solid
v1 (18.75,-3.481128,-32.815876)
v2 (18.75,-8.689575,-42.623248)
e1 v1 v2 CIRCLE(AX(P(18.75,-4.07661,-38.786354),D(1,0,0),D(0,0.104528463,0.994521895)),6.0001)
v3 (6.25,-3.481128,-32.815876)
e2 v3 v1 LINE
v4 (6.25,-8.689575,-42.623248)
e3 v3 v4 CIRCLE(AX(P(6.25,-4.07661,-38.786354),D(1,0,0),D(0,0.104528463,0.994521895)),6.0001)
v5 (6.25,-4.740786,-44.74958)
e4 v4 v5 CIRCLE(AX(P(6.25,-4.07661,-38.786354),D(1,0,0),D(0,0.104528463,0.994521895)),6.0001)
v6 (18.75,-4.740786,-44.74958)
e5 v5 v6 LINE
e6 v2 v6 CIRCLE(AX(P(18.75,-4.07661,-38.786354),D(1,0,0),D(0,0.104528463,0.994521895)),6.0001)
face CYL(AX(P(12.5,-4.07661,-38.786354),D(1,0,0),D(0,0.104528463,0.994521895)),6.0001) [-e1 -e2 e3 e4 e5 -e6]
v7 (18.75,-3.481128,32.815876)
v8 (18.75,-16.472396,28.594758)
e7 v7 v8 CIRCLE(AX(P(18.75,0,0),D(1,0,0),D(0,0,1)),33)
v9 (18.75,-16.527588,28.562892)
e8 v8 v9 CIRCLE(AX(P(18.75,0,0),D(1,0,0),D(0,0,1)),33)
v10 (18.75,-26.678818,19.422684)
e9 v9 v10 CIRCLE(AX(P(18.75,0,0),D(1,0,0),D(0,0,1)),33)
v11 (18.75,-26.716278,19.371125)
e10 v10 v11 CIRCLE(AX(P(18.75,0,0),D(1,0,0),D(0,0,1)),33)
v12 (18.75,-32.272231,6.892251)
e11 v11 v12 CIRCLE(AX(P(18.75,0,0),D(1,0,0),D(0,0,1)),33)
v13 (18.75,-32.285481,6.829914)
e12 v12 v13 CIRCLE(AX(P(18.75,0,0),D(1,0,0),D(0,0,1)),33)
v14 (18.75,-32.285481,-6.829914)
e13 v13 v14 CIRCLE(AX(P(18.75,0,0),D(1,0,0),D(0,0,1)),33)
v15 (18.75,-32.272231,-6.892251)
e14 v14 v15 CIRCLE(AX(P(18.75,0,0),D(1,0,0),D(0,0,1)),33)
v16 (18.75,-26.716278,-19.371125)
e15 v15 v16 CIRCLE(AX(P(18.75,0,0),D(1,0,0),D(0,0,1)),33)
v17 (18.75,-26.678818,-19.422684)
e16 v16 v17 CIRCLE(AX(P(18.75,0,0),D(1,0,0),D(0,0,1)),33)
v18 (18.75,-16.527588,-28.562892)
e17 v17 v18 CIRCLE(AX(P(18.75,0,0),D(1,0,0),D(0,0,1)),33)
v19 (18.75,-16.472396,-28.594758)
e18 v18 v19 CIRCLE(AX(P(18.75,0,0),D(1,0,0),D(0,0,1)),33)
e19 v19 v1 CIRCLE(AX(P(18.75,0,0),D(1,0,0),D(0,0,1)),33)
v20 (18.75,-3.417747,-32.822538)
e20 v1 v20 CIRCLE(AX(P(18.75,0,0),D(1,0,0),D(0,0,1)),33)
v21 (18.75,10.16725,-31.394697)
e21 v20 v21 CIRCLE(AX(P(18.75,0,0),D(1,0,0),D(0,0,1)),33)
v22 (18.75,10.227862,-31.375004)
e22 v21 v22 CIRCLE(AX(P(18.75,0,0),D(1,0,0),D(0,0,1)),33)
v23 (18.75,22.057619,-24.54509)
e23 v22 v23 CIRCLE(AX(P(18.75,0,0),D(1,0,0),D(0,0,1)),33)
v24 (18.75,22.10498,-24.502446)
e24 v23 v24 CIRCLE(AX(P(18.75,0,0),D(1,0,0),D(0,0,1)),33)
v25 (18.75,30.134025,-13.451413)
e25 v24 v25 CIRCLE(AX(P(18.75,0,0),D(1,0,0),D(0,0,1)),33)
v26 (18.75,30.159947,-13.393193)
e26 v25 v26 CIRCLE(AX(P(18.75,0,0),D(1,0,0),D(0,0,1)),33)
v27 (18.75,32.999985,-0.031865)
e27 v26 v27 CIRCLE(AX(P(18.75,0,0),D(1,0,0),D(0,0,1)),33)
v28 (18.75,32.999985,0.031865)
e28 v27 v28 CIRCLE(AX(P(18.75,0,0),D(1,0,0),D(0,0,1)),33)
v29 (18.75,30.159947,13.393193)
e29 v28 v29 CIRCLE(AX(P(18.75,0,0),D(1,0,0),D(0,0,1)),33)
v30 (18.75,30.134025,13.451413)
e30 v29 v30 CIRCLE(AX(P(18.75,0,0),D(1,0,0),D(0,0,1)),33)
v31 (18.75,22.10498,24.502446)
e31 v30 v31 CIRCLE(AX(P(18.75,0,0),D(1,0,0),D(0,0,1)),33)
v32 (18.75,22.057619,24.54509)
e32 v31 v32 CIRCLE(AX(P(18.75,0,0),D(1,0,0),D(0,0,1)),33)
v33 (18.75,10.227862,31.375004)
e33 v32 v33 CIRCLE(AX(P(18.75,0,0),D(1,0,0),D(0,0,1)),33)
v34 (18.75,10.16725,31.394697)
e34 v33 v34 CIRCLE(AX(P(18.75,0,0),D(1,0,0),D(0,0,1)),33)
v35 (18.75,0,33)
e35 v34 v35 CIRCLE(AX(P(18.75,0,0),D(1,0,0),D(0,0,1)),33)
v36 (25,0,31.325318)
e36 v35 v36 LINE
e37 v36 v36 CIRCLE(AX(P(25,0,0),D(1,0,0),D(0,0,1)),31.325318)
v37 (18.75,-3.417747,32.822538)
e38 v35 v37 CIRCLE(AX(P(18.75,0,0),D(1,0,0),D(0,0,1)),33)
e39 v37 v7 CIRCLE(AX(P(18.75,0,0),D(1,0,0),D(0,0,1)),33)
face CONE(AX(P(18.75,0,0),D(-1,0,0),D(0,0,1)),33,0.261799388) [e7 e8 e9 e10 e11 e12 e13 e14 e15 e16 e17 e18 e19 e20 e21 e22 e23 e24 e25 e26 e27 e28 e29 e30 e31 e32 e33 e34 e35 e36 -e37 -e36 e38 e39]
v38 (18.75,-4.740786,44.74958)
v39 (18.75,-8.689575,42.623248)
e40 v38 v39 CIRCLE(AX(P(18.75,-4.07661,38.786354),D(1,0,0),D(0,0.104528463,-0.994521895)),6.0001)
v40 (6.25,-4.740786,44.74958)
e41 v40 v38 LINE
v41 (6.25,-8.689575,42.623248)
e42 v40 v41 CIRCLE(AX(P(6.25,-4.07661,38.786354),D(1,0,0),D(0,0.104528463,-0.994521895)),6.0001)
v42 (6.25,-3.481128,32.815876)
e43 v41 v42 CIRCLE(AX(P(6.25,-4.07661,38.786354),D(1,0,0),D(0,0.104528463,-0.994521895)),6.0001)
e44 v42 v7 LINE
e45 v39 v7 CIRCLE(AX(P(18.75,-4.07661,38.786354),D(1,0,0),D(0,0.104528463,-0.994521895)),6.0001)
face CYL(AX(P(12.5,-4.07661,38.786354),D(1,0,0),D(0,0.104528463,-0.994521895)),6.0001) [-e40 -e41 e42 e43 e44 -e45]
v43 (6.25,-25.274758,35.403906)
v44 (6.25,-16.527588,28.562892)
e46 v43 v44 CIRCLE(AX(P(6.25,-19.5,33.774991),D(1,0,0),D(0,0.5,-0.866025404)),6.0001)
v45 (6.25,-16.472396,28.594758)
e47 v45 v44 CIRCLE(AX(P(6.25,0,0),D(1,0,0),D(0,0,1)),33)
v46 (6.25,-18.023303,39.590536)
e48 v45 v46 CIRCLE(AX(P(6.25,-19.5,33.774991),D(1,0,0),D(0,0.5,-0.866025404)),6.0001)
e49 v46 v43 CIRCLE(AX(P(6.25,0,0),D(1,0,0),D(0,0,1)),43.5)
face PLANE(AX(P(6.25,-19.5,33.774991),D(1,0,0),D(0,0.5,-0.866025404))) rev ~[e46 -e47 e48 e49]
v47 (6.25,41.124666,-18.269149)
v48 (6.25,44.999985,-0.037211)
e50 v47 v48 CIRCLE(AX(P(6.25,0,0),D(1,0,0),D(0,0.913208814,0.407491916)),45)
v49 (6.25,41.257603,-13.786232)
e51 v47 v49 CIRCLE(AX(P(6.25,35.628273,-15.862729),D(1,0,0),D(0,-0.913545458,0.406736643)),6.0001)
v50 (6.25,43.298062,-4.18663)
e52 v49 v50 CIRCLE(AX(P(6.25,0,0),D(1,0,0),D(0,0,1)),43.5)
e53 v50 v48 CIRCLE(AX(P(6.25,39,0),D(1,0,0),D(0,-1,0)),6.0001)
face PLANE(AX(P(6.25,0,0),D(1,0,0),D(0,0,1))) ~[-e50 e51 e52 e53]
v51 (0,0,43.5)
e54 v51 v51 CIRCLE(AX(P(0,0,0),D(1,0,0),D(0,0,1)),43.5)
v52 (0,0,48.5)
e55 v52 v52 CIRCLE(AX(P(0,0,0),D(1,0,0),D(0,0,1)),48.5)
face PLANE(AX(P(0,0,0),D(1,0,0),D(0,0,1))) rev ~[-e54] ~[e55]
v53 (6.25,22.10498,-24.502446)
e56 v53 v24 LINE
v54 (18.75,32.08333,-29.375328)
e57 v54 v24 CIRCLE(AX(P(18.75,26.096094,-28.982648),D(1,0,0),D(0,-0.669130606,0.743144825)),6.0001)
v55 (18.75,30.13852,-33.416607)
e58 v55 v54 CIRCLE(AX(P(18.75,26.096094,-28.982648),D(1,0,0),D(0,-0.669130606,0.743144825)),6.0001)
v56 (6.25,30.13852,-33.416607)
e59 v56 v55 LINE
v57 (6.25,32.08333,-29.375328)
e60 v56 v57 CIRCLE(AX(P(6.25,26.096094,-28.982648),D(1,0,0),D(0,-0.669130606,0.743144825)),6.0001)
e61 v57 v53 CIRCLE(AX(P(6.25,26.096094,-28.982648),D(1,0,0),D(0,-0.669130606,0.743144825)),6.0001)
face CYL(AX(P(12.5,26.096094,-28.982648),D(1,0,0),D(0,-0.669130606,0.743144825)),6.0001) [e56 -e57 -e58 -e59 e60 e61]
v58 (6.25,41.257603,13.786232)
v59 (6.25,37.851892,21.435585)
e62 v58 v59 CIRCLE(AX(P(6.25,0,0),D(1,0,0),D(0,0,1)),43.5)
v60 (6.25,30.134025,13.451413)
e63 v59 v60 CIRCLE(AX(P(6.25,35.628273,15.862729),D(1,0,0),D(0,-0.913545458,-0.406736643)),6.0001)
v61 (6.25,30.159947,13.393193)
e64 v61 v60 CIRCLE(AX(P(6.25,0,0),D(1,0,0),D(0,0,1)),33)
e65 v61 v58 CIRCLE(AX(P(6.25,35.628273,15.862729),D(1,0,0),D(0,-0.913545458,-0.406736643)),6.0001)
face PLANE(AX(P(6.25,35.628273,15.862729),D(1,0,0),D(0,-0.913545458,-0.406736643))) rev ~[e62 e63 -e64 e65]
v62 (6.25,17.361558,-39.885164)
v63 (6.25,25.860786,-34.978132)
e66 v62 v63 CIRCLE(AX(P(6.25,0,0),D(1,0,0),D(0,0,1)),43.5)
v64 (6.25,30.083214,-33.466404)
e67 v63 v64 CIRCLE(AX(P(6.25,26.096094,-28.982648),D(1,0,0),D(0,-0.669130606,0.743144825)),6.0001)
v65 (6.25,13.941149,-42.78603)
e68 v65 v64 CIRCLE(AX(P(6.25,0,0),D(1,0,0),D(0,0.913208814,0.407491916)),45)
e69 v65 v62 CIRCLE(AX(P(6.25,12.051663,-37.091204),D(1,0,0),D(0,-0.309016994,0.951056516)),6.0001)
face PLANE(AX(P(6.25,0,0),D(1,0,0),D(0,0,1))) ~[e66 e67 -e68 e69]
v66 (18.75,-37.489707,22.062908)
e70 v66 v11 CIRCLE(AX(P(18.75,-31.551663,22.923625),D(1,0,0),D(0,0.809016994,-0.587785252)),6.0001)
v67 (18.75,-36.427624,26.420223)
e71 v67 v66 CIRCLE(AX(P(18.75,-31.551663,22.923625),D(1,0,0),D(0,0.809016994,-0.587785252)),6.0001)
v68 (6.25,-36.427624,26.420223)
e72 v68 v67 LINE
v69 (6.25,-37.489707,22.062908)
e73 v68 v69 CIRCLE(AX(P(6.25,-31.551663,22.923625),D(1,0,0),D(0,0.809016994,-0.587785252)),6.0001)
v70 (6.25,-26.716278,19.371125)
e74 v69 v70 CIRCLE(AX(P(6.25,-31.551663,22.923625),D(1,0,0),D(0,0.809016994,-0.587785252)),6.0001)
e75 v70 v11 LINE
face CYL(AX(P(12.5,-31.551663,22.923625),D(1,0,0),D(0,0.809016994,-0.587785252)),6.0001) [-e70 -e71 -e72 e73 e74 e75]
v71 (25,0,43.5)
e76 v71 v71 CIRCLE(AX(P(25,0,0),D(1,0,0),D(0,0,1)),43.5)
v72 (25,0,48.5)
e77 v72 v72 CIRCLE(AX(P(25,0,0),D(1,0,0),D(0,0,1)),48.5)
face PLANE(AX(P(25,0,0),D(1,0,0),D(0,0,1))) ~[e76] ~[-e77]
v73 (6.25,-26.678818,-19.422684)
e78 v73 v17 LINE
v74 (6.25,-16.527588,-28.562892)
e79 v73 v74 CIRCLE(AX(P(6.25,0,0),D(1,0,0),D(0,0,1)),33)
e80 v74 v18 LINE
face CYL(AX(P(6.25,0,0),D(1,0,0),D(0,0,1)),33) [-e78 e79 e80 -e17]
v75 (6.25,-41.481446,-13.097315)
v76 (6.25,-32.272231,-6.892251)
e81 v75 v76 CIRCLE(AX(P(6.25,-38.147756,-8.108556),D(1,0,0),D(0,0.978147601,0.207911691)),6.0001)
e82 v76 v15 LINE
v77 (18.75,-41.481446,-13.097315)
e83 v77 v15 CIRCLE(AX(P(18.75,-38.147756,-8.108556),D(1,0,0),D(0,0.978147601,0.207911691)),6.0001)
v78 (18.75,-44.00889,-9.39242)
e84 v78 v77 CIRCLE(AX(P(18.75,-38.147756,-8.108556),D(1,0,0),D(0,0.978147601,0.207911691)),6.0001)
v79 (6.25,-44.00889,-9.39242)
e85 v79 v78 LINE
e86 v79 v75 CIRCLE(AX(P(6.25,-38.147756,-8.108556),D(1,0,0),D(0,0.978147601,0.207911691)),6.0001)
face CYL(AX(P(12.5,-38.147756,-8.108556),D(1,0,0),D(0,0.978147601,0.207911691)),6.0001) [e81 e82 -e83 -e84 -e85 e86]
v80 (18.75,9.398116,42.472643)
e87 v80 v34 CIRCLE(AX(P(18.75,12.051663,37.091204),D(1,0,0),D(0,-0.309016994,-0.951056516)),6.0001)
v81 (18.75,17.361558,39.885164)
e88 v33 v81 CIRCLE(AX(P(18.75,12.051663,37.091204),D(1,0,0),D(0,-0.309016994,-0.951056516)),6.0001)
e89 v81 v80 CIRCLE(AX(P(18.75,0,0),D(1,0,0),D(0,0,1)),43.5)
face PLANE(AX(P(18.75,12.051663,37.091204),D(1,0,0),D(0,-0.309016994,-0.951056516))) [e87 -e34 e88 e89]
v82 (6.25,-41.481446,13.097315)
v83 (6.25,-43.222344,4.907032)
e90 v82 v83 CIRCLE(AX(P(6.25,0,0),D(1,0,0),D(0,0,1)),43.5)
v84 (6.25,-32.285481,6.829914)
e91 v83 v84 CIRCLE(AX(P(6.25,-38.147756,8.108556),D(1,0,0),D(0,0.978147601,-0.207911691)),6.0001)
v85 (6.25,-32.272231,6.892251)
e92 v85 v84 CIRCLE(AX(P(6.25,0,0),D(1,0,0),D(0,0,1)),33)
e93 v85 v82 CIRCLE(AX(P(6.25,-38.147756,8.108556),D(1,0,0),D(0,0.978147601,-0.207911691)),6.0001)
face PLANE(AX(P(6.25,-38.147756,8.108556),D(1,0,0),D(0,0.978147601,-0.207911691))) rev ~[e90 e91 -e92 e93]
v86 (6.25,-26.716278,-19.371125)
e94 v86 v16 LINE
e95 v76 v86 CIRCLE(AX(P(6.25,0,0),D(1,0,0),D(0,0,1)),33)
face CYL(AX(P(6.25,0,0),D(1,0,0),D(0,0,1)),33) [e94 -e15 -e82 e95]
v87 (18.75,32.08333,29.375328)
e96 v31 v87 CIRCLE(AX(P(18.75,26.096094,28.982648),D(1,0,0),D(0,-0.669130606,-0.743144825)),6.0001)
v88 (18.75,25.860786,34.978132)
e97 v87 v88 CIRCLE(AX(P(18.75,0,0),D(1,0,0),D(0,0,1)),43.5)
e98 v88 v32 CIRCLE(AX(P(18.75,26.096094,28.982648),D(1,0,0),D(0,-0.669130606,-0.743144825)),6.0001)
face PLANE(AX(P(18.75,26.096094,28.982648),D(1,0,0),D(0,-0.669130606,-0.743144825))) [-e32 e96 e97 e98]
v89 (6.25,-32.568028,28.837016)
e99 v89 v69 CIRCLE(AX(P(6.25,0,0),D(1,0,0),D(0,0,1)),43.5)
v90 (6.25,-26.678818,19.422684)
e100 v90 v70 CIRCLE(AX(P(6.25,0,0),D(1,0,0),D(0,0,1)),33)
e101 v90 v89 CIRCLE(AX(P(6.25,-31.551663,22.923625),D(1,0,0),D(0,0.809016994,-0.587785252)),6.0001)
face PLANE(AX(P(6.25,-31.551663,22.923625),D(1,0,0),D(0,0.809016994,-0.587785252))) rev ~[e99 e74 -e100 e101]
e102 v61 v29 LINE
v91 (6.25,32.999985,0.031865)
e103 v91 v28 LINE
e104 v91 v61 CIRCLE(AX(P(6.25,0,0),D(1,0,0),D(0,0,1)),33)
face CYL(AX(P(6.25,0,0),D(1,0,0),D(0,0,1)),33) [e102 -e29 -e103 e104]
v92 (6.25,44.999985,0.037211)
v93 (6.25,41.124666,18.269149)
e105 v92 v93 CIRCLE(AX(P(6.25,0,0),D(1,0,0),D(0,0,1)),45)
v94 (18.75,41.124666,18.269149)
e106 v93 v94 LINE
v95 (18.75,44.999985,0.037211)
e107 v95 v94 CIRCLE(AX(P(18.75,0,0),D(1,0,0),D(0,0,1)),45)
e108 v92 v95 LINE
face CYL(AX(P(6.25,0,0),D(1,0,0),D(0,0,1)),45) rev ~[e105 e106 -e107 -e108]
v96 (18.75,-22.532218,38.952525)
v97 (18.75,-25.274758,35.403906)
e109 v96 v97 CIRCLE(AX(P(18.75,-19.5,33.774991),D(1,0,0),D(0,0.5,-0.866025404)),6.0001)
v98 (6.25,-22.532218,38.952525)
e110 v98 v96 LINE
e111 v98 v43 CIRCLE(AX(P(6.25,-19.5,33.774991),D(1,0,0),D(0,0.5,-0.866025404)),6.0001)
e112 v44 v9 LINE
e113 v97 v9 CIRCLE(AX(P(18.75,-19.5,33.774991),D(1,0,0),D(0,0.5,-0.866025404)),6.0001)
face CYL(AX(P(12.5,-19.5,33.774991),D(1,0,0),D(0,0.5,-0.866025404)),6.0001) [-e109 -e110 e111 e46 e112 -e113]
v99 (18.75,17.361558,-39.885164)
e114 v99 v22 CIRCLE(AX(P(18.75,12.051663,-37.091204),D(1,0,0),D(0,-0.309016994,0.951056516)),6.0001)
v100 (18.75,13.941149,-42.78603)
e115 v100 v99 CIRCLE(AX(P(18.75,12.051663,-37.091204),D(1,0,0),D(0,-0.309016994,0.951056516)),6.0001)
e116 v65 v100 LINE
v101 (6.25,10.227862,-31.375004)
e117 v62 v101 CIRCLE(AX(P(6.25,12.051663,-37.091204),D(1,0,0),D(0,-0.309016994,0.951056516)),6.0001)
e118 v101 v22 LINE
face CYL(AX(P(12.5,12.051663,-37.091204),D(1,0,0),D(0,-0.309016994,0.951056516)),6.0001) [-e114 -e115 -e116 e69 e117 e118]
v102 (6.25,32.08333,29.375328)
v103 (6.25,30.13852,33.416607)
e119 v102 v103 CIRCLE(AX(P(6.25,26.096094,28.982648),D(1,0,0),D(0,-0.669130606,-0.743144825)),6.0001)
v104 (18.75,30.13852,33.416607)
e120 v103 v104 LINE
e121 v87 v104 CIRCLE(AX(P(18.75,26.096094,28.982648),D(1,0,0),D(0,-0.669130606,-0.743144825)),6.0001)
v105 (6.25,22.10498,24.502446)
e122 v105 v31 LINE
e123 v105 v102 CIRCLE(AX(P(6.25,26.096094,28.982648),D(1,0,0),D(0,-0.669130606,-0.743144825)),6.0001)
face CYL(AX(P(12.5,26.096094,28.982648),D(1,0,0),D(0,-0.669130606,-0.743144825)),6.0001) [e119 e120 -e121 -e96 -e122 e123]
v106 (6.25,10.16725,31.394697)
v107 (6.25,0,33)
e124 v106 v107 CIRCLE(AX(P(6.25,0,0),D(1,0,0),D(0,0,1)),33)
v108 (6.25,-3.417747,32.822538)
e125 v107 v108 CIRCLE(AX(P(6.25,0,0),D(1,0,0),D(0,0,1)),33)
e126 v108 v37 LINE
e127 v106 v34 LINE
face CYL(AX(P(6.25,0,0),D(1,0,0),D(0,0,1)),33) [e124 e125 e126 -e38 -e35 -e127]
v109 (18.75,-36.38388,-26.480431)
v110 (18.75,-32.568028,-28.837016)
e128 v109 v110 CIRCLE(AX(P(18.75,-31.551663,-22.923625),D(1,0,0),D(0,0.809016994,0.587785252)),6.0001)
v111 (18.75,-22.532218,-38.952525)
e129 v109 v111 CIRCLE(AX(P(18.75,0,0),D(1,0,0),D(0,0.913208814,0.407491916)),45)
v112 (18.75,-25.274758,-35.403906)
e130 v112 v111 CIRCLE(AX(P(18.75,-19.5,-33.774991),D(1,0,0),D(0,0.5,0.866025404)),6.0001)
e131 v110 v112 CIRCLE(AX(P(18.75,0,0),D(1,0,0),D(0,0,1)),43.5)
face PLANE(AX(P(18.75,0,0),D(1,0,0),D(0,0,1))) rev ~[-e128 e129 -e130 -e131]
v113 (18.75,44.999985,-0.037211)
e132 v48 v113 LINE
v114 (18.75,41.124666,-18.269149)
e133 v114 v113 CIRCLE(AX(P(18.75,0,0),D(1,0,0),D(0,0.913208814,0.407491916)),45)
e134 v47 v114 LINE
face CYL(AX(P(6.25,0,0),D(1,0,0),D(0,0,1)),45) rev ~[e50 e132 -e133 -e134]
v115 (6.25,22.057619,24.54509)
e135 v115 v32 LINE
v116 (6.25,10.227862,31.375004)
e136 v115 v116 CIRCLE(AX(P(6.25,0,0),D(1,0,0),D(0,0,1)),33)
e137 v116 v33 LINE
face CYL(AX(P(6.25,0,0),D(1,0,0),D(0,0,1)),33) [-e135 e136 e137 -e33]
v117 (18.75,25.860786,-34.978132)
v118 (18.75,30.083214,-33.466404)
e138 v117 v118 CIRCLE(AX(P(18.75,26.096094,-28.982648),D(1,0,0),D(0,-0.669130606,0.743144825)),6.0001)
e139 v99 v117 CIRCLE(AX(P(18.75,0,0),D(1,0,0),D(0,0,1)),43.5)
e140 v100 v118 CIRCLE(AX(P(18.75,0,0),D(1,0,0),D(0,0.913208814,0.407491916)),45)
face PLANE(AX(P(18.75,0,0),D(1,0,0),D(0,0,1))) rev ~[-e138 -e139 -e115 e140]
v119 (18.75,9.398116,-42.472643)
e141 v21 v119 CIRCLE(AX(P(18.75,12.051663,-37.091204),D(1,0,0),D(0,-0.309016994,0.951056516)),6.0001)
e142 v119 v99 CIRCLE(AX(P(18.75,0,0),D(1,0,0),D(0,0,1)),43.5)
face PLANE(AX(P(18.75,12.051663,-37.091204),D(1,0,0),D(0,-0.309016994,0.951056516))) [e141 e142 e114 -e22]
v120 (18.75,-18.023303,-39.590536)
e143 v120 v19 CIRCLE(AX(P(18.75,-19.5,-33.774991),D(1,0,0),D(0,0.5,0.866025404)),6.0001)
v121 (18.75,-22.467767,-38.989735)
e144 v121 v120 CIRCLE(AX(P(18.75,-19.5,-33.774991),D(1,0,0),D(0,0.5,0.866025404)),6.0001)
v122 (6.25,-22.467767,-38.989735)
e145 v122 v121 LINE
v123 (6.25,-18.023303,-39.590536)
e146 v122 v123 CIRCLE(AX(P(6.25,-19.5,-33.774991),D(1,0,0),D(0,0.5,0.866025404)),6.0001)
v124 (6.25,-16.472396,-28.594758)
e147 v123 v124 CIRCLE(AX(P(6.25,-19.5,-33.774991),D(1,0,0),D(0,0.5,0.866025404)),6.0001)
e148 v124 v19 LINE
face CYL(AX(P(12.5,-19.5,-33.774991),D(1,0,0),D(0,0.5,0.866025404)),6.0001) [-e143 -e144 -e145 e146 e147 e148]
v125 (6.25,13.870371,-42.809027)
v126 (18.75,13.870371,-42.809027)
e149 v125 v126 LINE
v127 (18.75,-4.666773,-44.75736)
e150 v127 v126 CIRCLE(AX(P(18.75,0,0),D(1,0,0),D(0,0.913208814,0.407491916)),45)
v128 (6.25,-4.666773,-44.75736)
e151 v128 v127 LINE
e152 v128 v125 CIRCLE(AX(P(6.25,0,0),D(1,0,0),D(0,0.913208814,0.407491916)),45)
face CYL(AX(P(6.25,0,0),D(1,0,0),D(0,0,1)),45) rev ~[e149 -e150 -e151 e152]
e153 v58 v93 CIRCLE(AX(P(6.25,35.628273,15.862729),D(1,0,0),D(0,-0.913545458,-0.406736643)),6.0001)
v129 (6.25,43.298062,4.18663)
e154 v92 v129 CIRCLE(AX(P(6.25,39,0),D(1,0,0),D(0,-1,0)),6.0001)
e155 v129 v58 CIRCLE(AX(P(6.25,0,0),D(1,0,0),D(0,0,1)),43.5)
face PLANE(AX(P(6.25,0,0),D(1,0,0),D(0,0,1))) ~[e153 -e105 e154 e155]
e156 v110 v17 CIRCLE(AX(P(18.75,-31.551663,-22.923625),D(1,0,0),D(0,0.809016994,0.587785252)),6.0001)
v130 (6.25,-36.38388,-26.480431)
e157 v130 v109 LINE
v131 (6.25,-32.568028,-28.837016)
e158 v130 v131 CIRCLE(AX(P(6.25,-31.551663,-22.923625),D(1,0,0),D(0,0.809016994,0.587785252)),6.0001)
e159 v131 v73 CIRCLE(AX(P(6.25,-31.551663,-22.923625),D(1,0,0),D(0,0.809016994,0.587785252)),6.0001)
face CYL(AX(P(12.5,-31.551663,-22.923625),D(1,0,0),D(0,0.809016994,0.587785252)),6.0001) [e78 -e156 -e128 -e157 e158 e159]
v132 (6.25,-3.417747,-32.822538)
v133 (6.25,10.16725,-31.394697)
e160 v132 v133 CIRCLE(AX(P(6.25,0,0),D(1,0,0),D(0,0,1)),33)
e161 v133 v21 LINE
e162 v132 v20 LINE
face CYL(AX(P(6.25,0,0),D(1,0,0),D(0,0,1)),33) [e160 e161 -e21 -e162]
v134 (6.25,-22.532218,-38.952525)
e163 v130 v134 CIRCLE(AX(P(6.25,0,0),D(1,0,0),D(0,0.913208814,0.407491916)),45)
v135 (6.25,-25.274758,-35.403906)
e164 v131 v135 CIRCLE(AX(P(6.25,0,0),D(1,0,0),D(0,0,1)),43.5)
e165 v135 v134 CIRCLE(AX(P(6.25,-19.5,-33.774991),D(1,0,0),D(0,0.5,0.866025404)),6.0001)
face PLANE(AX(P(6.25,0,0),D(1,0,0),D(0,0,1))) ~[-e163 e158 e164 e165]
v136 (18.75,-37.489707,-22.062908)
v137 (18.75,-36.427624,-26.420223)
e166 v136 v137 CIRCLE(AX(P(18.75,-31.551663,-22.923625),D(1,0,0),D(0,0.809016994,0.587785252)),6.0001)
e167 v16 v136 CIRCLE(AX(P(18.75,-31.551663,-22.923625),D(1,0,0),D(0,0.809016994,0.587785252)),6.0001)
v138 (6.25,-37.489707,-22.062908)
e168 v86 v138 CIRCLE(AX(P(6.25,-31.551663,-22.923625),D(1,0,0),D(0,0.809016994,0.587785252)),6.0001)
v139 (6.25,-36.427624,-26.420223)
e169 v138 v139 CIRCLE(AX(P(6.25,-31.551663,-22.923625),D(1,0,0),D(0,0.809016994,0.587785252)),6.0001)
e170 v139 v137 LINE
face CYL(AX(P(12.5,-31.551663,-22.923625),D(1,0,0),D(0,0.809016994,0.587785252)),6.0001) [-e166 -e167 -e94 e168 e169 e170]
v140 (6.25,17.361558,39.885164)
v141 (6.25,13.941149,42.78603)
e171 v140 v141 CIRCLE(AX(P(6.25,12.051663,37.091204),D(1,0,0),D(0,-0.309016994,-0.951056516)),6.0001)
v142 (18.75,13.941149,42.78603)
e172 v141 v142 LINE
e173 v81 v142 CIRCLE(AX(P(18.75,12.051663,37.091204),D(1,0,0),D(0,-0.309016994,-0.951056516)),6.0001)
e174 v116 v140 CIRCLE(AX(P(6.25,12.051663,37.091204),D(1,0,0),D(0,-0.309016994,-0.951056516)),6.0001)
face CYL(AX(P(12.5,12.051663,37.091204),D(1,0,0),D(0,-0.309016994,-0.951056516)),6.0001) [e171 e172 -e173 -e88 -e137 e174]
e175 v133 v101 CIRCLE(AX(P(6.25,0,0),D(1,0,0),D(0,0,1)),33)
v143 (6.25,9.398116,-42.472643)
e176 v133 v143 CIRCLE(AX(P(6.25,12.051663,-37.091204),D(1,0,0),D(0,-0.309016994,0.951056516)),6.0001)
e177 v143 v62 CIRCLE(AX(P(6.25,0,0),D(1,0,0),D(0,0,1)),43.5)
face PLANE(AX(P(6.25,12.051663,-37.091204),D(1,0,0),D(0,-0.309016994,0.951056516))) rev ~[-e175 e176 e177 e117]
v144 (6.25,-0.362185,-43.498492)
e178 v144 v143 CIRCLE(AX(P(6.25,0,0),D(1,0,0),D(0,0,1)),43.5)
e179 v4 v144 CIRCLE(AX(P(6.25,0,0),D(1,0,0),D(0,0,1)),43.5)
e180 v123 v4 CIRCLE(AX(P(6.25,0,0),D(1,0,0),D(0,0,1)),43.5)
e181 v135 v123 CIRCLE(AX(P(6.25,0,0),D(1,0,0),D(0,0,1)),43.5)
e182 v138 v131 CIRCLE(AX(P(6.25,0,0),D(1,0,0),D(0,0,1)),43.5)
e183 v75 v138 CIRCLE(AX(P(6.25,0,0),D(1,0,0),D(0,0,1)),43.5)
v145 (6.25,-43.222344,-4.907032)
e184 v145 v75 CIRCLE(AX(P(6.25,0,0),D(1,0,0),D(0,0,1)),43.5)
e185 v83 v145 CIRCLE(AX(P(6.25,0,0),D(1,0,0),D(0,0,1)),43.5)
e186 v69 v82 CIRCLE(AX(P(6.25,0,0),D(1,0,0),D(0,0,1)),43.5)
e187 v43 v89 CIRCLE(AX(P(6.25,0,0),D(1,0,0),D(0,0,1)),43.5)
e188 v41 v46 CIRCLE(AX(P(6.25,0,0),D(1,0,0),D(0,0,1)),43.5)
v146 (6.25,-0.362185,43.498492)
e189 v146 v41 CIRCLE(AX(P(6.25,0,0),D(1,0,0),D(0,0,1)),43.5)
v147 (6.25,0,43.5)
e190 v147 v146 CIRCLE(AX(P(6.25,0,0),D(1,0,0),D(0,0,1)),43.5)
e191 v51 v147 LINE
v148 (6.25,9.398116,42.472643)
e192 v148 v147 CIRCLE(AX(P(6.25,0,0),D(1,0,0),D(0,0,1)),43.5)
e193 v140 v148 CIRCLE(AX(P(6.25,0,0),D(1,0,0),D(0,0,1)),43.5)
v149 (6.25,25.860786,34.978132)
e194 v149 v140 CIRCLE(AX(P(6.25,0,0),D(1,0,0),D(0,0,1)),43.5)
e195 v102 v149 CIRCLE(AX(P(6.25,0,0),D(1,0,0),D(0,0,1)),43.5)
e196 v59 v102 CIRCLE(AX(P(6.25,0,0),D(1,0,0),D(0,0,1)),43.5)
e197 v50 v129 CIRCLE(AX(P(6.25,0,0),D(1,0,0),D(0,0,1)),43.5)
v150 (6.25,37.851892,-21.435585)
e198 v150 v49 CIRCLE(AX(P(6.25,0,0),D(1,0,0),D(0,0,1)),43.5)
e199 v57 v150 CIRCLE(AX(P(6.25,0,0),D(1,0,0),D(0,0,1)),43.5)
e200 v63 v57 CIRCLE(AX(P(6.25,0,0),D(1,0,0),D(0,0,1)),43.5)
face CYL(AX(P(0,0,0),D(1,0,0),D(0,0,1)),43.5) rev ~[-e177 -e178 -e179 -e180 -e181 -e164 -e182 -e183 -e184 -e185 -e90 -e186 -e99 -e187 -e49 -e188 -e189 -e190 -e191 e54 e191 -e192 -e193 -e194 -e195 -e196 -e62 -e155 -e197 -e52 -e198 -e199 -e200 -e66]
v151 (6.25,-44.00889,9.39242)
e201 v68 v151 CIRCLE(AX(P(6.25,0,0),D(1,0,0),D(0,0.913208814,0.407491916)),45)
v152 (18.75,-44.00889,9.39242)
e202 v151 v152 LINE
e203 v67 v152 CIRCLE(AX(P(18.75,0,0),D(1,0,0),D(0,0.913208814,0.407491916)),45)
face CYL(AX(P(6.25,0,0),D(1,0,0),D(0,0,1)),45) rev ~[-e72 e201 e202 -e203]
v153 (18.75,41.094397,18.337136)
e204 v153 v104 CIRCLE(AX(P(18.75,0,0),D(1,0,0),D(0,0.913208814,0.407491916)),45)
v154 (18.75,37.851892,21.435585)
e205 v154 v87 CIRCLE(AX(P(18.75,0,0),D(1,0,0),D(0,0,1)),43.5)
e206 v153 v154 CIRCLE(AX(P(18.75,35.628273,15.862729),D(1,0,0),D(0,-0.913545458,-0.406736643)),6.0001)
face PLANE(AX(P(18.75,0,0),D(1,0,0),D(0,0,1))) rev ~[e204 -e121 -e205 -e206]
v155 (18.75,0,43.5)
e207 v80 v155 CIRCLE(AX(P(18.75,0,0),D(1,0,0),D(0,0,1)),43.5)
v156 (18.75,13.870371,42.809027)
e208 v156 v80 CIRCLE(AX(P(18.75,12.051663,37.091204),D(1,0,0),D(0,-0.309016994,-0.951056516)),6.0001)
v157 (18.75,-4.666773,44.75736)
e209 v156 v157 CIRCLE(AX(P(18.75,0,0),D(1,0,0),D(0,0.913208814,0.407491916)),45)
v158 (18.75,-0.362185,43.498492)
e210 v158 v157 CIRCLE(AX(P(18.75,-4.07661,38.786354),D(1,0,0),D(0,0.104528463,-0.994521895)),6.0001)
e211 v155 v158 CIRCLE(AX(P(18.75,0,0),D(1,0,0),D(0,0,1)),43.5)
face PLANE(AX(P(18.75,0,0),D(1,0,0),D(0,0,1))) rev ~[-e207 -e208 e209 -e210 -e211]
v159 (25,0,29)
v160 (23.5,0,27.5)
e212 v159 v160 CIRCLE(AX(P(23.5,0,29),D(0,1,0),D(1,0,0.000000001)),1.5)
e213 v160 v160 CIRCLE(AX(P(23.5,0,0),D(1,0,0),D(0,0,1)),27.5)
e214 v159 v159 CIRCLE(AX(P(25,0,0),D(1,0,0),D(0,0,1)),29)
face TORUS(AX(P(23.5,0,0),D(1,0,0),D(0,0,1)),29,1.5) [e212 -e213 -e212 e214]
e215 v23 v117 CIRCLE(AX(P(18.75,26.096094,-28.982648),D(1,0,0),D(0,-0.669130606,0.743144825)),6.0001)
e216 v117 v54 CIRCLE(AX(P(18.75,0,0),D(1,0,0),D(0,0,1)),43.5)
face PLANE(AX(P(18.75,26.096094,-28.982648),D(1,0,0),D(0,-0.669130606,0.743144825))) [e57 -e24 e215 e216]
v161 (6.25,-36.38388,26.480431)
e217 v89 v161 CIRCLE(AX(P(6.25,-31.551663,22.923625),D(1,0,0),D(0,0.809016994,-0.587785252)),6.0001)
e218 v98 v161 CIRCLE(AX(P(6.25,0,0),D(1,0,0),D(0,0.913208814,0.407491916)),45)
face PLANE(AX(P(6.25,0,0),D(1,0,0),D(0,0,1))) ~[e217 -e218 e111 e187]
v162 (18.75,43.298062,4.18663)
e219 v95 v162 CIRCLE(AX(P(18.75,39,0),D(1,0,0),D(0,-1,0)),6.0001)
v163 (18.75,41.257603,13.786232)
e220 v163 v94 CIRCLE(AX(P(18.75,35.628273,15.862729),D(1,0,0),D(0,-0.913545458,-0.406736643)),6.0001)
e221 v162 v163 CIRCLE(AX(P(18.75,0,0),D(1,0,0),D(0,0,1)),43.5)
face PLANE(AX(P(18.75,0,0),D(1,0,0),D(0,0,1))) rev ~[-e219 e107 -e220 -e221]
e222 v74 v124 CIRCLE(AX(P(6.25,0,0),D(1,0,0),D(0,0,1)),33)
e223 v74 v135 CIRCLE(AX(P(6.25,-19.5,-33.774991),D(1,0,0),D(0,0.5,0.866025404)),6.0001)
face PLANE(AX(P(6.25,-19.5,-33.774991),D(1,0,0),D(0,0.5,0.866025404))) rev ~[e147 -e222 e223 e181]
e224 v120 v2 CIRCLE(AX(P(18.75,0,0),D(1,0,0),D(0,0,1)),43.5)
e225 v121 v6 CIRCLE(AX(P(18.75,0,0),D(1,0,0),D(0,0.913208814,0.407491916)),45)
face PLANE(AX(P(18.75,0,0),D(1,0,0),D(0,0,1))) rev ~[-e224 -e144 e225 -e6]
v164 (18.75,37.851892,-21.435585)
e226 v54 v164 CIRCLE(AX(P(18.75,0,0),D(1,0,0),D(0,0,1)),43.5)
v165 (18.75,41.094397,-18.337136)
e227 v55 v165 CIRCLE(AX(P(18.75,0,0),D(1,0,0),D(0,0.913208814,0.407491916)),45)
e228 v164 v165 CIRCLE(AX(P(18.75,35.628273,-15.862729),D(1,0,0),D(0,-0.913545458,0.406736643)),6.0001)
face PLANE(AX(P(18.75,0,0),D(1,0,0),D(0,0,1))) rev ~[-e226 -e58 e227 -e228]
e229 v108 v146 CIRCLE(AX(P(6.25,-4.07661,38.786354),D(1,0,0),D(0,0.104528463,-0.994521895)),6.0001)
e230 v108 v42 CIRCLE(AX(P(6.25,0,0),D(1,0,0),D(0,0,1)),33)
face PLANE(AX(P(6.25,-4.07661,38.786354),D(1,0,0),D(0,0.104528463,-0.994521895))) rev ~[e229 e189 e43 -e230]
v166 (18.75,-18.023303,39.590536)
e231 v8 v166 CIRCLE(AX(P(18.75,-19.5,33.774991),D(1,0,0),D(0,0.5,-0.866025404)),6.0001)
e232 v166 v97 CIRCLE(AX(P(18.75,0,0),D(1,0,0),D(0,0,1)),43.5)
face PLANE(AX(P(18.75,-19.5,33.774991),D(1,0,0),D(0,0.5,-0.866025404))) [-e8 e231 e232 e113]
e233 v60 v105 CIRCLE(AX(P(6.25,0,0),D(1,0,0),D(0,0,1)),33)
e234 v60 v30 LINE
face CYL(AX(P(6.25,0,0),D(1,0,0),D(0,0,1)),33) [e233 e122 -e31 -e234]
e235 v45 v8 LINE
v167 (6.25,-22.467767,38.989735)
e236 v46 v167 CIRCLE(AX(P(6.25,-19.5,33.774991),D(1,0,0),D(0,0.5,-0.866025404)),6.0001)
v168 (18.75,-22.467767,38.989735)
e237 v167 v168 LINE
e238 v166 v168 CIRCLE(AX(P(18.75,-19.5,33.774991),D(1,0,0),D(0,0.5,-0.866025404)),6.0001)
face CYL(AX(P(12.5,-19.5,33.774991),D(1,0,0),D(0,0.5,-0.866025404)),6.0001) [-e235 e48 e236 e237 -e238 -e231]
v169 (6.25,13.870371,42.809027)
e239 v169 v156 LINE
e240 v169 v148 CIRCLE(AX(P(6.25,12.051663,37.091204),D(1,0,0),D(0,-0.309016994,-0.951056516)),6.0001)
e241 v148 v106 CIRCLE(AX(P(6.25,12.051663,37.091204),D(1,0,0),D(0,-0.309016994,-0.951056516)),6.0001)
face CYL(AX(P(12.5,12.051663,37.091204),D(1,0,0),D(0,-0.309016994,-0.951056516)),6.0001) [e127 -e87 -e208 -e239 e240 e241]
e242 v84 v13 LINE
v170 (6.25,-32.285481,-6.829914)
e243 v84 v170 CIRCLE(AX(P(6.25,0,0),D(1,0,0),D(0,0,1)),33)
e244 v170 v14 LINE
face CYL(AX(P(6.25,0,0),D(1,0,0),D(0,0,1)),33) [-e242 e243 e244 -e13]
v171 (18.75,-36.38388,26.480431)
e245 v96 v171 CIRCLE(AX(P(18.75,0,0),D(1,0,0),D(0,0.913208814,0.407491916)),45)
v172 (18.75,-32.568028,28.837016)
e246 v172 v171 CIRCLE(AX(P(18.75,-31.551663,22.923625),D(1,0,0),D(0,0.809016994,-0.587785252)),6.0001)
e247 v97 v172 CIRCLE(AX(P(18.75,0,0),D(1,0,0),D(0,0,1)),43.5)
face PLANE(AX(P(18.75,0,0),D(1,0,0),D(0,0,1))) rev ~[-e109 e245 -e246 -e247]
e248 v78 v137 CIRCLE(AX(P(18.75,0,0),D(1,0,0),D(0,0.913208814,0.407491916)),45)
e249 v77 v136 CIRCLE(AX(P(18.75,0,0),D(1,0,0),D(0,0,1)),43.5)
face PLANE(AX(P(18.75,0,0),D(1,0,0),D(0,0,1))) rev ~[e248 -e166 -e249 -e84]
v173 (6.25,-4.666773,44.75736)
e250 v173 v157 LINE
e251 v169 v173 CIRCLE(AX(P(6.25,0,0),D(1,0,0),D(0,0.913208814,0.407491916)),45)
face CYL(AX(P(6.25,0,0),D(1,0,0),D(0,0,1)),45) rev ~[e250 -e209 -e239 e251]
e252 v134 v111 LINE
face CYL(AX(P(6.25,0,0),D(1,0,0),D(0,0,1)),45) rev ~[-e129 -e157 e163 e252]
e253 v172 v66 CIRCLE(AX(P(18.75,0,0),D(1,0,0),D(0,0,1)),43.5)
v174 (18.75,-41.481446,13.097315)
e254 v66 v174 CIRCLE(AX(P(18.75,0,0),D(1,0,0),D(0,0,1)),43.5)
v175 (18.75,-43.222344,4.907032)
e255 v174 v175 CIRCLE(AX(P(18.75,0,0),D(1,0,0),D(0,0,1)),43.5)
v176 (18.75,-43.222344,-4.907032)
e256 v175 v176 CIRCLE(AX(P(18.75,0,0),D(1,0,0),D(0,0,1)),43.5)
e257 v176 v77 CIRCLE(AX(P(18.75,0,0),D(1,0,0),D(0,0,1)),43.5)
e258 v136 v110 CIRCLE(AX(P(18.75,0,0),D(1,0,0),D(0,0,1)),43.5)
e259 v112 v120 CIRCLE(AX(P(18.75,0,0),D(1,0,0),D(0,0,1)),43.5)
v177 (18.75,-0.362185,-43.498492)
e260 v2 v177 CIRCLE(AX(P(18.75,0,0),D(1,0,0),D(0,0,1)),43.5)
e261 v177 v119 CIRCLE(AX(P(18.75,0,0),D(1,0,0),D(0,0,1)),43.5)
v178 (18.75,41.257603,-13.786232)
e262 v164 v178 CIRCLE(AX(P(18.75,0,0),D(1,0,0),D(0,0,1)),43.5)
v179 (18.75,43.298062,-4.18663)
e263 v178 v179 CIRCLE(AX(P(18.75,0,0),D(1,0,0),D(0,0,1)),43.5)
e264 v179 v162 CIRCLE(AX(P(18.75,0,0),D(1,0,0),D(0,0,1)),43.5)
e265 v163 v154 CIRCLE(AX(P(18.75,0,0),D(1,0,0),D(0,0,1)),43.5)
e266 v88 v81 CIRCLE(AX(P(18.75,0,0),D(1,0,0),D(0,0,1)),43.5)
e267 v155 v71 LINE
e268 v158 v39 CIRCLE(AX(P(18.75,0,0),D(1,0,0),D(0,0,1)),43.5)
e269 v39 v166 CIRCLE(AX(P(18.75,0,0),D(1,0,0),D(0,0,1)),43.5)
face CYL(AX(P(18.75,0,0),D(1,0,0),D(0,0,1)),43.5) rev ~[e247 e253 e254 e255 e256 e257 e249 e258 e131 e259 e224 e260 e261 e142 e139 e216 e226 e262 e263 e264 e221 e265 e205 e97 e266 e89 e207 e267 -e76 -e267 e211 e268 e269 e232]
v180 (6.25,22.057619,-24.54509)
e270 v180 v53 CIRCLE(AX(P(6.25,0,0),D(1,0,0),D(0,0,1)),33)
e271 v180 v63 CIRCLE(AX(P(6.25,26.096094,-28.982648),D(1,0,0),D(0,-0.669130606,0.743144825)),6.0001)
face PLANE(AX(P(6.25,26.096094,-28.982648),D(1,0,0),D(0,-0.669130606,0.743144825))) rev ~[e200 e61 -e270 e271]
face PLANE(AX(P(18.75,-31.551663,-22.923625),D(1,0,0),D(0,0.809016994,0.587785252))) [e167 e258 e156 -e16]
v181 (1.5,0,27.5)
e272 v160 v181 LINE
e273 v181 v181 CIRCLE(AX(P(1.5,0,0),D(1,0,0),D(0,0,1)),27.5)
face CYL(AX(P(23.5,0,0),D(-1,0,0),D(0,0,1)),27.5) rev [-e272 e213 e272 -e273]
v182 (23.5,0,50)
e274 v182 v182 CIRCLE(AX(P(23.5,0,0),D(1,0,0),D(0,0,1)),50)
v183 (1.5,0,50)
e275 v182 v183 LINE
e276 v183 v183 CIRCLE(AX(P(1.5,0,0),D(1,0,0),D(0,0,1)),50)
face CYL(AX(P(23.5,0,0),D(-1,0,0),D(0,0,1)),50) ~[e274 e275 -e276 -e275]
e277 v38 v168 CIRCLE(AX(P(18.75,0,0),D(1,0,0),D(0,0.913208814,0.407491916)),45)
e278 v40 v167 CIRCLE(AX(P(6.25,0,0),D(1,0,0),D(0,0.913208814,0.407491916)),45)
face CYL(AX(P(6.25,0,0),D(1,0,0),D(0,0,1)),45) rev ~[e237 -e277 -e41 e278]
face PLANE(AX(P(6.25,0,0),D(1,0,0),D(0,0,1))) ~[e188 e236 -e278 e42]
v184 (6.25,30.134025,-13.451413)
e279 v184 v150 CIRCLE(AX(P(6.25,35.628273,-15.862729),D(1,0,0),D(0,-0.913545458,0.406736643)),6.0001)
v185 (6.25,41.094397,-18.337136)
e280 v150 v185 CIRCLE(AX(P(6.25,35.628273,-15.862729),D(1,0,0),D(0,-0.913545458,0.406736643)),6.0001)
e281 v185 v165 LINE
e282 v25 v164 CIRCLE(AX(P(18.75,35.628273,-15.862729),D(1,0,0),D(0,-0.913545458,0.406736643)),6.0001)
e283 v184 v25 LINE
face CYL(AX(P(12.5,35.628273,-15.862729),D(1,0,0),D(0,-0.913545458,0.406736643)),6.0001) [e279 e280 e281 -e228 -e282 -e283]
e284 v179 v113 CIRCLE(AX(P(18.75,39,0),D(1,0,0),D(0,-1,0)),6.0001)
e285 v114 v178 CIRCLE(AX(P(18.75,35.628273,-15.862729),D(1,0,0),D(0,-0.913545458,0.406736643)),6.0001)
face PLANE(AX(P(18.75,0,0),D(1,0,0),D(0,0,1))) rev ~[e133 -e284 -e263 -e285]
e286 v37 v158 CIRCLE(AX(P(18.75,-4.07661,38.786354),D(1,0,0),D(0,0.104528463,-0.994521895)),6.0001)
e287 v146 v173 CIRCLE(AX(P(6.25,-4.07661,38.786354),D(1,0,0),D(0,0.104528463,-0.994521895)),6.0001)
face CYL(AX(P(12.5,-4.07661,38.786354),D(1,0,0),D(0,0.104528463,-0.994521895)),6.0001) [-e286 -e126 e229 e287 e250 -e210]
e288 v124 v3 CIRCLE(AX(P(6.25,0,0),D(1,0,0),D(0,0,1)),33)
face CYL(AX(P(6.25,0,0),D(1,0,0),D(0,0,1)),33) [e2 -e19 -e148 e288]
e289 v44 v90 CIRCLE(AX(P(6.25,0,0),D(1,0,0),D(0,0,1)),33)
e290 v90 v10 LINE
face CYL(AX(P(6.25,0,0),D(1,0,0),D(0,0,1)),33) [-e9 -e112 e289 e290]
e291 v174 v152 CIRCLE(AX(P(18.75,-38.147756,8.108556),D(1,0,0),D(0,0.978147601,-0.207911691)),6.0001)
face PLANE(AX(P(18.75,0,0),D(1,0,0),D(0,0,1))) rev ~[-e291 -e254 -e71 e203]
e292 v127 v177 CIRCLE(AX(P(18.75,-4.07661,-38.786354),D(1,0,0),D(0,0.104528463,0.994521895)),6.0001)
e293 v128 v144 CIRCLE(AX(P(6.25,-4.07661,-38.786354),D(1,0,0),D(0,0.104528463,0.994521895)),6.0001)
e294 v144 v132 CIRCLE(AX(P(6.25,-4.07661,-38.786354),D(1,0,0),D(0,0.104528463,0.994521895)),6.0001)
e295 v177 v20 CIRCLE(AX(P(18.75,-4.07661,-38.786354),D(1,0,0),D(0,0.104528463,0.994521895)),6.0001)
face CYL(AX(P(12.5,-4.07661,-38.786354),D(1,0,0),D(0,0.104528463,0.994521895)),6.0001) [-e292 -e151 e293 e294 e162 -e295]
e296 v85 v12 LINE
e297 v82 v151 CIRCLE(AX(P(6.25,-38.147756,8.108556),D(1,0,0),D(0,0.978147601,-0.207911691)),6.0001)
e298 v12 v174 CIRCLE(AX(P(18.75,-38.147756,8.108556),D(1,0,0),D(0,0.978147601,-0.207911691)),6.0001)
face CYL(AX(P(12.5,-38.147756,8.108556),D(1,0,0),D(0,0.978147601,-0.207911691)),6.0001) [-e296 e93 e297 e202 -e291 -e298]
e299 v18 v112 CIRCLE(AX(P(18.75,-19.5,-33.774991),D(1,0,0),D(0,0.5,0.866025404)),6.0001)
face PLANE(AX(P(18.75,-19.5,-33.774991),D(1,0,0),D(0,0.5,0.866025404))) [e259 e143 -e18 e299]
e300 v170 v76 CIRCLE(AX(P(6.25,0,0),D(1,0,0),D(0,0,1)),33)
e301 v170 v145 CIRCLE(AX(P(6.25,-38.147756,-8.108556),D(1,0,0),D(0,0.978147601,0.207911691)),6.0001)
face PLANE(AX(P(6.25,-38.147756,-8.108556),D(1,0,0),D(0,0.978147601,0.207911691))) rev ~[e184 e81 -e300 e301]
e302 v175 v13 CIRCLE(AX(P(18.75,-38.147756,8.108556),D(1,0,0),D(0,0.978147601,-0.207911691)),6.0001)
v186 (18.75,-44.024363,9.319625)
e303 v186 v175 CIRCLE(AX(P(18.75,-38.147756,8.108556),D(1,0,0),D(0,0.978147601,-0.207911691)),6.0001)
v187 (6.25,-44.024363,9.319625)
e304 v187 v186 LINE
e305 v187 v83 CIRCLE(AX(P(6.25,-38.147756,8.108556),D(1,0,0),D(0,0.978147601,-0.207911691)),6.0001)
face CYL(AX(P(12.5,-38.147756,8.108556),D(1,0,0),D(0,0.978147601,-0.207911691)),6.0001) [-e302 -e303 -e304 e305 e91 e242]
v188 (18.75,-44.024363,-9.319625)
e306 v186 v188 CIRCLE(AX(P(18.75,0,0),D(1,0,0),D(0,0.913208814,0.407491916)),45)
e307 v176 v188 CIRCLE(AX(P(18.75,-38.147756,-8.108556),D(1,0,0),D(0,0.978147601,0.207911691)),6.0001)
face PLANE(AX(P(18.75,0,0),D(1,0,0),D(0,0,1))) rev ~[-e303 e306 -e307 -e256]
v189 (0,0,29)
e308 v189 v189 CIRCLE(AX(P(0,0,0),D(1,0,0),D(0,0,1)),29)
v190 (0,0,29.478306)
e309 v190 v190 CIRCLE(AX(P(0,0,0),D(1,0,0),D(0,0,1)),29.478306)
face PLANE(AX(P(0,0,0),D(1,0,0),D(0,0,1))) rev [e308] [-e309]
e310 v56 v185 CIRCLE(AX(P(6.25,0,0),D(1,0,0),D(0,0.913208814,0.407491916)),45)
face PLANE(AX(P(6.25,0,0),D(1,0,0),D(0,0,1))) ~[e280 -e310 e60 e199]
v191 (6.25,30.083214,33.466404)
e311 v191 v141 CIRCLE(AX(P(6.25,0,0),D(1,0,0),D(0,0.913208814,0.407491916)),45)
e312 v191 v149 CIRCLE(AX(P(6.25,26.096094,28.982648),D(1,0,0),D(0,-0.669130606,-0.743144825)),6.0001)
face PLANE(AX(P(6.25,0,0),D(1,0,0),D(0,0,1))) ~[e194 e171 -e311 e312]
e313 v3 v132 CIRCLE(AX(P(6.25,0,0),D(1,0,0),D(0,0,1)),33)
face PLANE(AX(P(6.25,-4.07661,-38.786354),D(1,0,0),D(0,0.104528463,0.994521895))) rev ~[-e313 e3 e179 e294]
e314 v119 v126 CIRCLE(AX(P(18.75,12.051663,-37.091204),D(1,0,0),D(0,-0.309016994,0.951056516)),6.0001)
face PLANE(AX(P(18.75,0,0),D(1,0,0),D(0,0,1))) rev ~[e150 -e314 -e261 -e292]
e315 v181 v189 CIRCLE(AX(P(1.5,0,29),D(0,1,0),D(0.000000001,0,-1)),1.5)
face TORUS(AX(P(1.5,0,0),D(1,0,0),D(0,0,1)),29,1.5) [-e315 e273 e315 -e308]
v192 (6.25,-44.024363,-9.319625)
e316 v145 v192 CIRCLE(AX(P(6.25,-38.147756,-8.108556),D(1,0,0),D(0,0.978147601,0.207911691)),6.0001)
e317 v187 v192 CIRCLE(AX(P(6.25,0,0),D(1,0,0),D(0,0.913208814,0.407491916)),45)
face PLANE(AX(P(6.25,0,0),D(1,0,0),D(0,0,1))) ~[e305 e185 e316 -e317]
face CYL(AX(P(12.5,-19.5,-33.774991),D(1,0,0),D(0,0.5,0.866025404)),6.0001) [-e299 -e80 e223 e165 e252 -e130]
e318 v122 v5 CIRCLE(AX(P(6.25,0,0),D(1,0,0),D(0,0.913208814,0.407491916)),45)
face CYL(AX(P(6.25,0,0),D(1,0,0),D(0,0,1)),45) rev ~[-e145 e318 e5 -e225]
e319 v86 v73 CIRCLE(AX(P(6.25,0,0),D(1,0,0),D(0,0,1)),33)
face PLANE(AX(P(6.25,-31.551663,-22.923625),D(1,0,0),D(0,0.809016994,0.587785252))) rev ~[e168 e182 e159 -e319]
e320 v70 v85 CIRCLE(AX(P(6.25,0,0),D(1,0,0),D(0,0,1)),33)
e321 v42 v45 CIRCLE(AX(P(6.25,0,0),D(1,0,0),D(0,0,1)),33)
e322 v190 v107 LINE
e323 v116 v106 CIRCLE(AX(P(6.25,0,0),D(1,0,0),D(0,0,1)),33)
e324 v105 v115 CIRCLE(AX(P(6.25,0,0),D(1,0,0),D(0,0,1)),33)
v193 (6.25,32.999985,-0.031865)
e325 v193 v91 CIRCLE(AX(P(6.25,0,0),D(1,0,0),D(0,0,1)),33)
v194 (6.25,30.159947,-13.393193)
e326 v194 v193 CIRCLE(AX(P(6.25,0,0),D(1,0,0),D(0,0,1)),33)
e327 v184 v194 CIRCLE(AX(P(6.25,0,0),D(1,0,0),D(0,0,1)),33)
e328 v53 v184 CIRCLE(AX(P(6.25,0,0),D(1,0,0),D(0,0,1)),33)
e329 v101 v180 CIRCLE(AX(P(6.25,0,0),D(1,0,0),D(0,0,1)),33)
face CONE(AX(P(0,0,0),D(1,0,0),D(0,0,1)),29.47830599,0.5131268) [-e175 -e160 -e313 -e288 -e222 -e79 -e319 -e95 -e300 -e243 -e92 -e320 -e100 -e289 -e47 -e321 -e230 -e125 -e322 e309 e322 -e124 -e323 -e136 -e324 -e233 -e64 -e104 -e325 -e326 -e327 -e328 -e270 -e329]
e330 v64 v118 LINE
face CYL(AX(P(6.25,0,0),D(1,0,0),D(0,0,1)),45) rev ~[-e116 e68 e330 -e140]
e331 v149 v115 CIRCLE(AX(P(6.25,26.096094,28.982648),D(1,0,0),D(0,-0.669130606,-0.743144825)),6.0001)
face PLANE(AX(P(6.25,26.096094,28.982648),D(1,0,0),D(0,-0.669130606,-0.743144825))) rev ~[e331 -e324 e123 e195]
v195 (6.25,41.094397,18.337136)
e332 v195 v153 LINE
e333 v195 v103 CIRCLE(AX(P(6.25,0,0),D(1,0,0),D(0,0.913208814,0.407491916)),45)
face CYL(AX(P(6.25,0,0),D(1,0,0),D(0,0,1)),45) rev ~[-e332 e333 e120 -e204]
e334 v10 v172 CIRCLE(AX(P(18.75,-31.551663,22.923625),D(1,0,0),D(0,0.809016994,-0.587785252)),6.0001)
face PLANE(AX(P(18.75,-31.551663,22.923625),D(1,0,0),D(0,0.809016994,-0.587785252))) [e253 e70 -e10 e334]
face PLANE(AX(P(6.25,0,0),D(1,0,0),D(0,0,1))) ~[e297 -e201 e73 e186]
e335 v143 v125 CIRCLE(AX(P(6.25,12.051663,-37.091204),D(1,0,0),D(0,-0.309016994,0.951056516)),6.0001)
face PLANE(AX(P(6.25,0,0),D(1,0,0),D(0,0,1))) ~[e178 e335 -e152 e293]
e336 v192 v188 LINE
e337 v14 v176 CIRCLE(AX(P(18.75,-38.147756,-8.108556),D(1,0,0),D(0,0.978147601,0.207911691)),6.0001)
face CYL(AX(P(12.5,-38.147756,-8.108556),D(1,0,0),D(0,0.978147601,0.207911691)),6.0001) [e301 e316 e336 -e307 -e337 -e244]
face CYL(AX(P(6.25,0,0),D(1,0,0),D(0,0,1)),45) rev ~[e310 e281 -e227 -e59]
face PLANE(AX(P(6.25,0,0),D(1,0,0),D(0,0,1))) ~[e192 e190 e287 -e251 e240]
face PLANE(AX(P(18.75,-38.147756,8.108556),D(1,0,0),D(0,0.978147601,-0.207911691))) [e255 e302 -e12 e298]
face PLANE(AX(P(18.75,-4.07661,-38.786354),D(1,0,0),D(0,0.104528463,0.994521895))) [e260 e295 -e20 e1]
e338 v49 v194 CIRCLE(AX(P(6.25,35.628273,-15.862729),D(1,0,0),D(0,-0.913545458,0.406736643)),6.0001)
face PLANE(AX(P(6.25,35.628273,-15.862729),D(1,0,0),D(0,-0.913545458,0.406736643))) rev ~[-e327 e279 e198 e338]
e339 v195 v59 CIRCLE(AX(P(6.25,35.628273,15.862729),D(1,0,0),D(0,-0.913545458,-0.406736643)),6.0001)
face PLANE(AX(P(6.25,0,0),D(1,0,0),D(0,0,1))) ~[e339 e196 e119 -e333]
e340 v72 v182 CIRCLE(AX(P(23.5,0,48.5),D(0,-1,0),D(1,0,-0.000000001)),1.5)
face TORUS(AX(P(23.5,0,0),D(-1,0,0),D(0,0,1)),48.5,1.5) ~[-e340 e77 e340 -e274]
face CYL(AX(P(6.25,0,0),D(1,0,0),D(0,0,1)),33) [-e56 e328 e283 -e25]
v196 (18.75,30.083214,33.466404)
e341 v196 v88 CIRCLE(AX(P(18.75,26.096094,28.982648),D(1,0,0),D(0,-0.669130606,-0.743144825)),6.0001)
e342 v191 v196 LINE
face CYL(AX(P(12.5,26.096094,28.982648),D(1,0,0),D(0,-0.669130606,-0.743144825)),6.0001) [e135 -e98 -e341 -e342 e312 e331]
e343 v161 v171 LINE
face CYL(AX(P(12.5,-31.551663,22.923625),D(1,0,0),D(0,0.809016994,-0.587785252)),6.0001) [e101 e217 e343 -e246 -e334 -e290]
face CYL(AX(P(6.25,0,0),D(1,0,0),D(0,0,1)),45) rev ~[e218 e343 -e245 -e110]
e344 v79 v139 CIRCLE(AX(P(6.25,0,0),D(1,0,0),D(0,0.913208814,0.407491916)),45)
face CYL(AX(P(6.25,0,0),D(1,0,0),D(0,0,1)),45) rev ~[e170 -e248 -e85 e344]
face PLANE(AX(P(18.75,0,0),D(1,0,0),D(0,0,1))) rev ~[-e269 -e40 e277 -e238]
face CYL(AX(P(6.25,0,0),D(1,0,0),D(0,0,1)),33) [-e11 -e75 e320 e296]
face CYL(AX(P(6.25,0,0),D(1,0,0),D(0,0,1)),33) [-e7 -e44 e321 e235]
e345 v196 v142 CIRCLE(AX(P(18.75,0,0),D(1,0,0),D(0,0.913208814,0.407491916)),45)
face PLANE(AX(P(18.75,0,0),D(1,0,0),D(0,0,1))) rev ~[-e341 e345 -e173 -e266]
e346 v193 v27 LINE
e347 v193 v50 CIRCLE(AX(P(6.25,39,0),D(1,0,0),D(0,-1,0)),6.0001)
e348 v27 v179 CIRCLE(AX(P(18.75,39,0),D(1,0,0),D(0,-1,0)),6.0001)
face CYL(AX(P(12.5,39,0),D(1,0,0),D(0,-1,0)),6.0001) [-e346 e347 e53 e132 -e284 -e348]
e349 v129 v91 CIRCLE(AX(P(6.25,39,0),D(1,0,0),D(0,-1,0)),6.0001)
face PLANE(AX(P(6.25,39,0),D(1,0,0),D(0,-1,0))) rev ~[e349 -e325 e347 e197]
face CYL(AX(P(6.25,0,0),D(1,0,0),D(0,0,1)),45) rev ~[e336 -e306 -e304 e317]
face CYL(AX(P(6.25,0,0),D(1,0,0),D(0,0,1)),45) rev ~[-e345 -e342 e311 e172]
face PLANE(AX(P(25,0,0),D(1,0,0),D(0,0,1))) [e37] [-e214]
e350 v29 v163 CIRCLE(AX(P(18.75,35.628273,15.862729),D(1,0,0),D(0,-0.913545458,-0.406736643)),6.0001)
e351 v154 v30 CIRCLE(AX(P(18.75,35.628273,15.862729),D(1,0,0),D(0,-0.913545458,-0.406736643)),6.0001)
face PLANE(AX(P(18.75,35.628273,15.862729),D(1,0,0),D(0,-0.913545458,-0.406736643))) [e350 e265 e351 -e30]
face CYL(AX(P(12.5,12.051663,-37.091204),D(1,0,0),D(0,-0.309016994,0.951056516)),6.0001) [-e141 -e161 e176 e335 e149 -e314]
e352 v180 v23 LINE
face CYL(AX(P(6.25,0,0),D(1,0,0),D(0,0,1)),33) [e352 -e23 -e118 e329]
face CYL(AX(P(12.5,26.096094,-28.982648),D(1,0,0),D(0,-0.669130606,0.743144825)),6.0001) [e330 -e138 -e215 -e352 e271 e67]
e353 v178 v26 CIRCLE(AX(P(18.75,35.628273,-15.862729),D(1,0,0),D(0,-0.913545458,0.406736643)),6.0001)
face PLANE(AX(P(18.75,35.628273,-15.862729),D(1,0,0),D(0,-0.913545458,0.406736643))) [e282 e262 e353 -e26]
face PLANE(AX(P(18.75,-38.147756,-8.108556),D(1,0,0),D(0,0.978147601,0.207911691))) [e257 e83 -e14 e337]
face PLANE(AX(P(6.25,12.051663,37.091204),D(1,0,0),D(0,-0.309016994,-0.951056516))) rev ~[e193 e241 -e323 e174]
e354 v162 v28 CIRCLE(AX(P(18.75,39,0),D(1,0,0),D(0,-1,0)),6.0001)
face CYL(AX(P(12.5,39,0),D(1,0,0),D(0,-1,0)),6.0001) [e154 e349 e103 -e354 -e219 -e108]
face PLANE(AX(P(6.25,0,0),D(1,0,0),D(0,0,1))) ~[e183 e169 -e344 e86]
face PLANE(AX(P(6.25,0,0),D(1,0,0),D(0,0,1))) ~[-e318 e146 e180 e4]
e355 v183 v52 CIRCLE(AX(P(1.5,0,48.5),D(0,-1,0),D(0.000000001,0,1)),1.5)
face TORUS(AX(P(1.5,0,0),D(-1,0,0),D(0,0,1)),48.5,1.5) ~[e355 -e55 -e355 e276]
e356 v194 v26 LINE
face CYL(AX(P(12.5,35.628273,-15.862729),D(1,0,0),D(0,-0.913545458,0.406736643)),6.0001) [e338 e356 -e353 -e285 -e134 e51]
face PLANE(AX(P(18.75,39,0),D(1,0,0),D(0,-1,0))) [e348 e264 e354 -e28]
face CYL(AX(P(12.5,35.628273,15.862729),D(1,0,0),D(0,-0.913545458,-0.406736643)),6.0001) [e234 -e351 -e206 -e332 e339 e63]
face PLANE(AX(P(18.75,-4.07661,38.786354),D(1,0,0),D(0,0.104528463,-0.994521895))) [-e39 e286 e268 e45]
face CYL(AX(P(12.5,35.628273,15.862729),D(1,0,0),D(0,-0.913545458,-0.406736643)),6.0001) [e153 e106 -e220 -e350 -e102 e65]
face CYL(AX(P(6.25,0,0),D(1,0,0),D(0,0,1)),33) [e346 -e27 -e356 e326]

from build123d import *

# Parameters (mm, degrees)
SKETCH3_W         = 12.5
SKETCH3_H         = 6.0001
CIRPATTERN1_COUNT = 15


with BuildPart() as part:
    # Sketch2 → Base-Revolve (revolve)
    with BuildSketch(Plane.XY, mode=Mode.PRIVATE) as base_revolve_sk:
        with BuildLine():
            Line((6.25, 33), (18.75, 33))
            Line((18.75, 33), (25, 31.325317547))
            Line((25, 31.325317547), (25, 29))
            ThreePointArc((25, 29), (24.560660172, 27.939339828), (23.5, 27.5))
            Line((23.5, 27.5), (1.5, 27.5))
            ThreePointArc((1.5, 27.5), (0.439339828, 27.939339828), (0, 29))
            Line((0, 29), (0, 29.47830599))
            Line((0, 29.47830599), (6.25, 33))
        make_face()
    revolve(base_revolve_sk.sketch.rotate(Axis((-10.080094127, 0, 0), (1, 0, 0)), 90), axis=Axis((-10.080094127, 0, 0), (1, 0, 0)))

    # Sketch3 → Boss-Revolve1 (revolve)
    with BuildSketch(Plane.XY):
        with Locations((12.5, 35.99995)):
            Rectangle(SKETCH3_W, SKETCH3_H)
    boss_revolve1 = revolve(axis=Axis((-1.603948851, 39, 0), (1, 0, 0)))

    # Sketch4 → Boss-Revolve2 (revolve)
    with BuildSketch(Plane.XY, mode=Mode.PRIVATE) as boss_revolve2_sk:
        with BuildLine():
            Line((18.75, 43.5), (25, 43.5))
            Line((25, 43.5), (25, 48.5))
            ThreePointArc((25, 48.5), (24.560660172, 49.560660172), (23.5, 50))
            Line((23.5, 50), (1.5, 50))
            ThreePointArc((1.5, 50), (0.439339828, 49.560660172), (0, 48.5))
            Line((0, 48.5), (0, 43.5))
            Line((0, 43.5), (6.25, 43.5))
            Line((6.25, 43.5), (6.25, 45))
            Line((6.25, 45), (18.75, 45))
            Line((18.75, 45), (18.75, 43.5))
        make_face()
    revolve(boss_revolve2_sk.sketch.rotate(Axis((0, 0, 0), (1, 0, 0)), 90), axis=Axis((0, 0, 0), (1, 0, 0)))

    # CirPattern1: Boss-Revolve1 ×15 about axis
    cirpattern1_axis = Axis((0, 0, 0), (1, 0, 0))
    for i in range(1, CIRPATTERN1_COUNT):
        add(boss_revolve1.rotate(cirpattern1_axis, i * 360 / CIRPATTERN1_COUNT))


solid = part.part
